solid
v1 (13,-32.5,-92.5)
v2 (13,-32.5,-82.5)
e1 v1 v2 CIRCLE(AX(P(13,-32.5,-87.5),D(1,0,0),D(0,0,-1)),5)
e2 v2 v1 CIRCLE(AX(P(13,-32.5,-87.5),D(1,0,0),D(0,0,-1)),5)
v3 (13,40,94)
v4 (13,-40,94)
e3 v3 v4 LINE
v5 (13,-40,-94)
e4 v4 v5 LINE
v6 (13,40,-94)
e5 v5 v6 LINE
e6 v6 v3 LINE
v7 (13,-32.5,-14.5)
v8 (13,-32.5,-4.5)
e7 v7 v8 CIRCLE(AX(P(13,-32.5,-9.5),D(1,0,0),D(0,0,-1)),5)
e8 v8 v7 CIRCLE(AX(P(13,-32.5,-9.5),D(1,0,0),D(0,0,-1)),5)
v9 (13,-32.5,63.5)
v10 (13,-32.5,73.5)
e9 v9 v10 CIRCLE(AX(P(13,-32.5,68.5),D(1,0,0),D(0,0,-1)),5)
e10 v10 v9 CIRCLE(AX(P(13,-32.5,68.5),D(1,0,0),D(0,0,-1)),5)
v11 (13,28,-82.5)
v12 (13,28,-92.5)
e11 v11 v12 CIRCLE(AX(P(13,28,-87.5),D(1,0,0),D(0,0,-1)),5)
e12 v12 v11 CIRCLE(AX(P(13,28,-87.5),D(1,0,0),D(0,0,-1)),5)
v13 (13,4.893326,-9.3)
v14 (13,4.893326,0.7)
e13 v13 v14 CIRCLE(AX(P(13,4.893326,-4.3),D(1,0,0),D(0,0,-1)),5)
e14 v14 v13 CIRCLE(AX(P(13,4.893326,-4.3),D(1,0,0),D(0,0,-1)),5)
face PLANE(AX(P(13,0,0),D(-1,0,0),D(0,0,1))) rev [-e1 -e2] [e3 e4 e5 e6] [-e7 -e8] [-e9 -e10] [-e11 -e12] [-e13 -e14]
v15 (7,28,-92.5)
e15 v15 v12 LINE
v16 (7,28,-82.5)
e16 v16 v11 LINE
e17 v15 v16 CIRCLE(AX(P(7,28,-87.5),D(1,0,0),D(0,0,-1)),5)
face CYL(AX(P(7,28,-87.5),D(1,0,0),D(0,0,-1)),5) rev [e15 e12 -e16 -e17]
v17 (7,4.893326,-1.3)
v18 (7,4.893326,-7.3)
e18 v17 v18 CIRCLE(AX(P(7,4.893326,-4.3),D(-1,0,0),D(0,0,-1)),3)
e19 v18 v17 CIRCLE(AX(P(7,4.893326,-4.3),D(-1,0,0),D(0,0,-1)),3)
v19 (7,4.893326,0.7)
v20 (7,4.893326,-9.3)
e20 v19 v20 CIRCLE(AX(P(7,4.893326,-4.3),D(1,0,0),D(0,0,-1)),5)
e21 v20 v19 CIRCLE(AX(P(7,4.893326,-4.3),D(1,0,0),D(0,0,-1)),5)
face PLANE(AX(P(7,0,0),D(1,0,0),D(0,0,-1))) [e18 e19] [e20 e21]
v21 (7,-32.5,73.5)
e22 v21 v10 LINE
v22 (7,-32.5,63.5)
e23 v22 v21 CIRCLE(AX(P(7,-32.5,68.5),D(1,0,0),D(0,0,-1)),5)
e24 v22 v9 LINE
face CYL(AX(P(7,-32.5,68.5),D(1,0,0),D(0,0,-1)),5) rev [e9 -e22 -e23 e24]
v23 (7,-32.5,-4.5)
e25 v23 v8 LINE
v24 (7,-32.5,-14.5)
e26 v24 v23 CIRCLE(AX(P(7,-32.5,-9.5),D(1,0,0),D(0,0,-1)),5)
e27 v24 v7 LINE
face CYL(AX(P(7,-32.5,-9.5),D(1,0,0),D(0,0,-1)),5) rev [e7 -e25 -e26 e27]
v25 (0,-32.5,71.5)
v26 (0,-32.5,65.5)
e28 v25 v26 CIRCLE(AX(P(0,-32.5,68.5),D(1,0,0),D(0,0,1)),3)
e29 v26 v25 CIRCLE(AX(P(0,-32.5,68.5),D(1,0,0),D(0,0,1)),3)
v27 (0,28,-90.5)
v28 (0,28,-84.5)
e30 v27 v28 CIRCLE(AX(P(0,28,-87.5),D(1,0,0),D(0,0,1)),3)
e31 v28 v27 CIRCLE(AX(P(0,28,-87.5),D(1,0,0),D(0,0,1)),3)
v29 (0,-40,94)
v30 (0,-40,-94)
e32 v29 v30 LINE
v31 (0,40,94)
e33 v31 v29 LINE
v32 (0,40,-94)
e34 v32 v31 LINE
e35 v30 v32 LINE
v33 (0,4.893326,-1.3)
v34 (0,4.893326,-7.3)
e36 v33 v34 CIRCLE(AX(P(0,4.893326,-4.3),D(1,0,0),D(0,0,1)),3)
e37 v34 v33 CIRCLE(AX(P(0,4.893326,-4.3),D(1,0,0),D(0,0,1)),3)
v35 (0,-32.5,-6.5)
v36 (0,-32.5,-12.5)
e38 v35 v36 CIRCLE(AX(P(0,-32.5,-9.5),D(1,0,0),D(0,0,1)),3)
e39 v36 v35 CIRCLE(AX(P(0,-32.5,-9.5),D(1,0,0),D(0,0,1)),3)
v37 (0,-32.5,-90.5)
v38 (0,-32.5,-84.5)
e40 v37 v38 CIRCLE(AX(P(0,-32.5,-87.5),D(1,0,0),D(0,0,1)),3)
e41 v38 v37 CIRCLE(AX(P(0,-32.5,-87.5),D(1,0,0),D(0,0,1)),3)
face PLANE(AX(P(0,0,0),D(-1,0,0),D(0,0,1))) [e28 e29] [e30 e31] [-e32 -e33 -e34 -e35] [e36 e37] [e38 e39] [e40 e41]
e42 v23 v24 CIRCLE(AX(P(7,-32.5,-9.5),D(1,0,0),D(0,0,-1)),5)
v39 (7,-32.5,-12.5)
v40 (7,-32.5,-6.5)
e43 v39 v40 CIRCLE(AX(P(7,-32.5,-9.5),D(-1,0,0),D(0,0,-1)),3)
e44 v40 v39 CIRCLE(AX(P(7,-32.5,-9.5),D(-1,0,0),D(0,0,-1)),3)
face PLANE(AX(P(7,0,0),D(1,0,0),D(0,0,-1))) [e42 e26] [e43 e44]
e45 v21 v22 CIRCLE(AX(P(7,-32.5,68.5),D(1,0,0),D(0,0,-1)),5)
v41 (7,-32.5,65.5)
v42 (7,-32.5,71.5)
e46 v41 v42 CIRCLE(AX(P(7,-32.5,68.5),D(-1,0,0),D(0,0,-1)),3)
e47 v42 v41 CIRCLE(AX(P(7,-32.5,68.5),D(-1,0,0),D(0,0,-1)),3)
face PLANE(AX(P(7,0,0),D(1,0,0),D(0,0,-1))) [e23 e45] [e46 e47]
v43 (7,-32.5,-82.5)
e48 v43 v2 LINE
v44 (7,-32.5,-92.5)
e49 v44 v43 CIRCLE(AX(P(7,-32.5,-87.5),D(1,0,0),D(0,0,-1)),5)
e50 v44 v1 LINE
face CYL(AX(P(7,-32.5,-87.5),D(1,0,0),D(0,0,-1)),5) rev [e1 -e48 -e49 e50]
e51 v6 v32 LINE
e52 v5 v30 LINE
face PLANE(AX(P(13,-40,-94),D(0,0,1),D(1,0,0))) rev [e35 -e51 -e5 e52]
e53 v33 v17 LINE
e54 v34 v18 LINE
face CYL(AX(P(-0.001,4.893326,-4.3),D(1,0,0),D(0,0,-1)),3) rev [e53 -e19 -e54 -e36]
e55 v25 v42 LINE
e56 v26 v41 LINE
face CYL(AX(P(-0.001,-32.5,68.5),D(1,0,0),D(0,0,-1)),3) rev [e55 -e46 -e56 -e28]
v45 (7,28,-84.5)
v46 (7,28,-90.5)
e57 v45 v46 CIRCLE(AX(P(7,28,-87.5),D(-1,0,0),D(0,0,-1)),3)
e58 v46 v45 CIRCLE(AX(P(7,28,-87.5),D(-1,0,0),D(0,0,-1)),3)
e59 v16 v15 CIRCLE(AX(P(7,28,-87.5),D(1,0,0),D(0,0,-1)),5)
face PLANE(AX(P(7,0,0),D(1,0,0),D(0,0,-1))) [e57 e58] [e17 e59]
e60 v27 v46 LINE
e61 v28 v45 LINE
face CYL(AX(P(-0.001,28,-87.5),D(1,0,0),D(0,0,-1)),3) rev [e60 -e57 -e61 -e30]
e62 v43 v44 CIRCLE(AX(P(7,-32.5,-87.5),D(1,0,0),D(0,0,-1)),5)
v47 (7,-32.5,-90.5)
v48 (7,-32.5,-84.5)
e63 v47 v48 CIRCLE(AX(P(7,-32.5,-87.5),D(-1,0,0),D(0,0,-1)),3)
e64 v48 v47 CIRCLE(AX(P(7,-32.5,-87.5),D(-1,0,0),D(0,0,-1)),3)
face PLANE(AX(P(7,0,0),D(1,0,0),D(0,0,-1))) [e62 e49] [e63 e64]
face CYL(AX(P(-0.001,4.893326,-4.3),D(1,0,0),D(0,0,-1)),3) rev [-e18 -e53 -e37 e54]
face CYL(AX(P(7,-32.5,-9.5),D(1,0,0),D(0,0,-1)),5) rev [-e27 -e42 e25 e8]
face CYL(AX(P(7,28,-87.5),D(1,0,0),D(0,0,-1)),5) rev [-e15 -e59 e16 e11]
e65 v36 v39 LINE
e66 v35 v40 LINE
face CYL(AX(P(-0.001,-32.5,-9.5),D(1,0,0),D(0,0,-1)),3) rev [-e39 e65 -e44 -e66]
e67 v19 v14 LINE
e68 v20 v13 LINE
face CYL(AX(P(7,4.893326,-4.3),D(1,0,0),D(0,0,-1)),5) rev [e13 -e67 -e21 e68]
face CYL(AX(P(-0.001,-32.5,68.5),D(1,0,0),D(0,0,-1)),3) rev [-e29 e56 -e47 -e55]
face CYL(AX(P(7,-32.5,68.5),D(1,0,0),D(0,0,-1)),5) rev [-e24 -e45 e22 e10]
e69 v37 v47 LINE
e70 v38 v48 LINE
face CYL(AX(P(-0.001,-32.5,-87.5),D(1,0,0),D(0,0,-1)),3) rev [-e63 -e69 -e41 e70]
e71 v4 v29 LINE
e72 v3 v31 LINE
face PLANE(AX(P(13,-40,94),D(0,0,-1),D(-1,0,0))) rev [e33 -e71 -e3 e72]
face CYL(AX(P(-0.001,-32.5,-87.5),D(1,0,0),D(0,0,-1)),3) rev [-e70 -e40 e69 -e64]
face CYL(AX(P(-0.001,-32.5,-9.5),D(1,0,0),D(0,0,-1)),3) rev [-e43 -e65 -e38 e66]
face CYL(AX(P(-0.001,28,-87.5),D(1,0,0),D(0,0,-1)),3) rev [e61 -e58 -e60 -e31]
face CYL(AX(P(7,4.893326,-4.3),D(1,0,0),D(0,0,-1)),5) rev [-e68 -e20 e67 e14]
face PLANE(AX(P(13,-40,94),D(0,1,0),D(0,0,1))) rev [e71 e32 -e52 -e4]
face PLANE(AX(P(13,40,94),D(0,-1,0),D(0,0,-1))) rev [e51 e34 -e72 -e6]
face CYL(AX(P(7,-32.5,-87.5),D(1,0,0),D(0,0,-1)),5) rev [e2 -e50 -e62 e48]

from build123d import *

# Parameters (mm, degrees)
SKETCH1_W           = 188
SKETCH1_H           = 80
BOSS_EXTRUDE1_DEPTH = 13
SKETCH3_R           = 5
SKETCH3_R_2         = 3
CUT_EXTRUDE1_DEPTH  = 6
CUT_EXTRUDE2_REACH  = 104.981
SKETCH3_3_R         = 3
SKETCH4_R           = 5
SKETCH4_R_2         = 3
CUT_EXTRUDE3_DEPTH  = 6
CUT_EXTRUDE4_REACH  = 104.981
SKETCH4_3_R         = 3
SKETCH5_R           = 5
SKETCH5_R_2         = 3
CUT_EXTRUDE5_DEPTH  = 6
CUT_EXTRUDE6_REACH  = 104.981
SKETCH5_3_R         = 3


with BuildPart() as part:
    # Sketch1 → Boss-Extrude1 (new body)
    with BuildSketch(Plane(origin=(0, 0, 0), x_dir=(0, 0, -1), z_dir=(1, 0, 0))):
        Rectangle(SKETCH1_W, SKETCH1_H)
    extrude(amount=BOSS_EXTRUDE1_DEPTH)

    # Sketch3 → Cut-Extrude1 (cut)
    with BuildSketch(Plane(origin=(13, 0, 0), x_dir=(0, 0, -1), z_dir=(1, 0, 0))):
        with Locations((4.3, 4.893325501)):
            Circle(SKETCH3_R)
        with Locations((4.3, 4.893325501)):
            Circle(SKETCH3_R_2, mode=Mode.SUBTRACT)
    extrude(amount=-CUT_EXTRUDE1_DEPTH, mode=Mode.SUBTRACT)

    # Sketch3<3> → Cut-Extrude2 (cut, up to next)
    with BuildSketch(Plane(origin=(13, 0, 0), x_dir=(0, 0, -1), z_dir=(1, 0, 0)), mode=Mode.PRIVATE) as cut_extrude2_sk1:
        with Locations((4.3, 4.893325501)):
            Circle(SKETCH3_3_R)
    cut_extrude2_tool1 = extrude(cut_extrude2_sk1.sketch, amount=-CUT_EXTRUDE2_REACH, mode=Mode.PRIVATE) & part.part
    add(cut_extrude2_tool1.solids().sort_by_distance((13, 4.893326, -4.3))[0], mode=Mode.SUBTRACT)

    # Sketch4 → Cut-Extrude3 (cut)
    # profile 1 of 3: a face of its own
    with BuildSketch(Plane(origin=(13, 0, 0), x_dir=(0, 0, -1), z_dir=(1, 0, 0))):
        with Locations((-68.5, -32.5)):
            Circle(SKETCH4_R)
        with Locations((-68.5, -32.5)):
            Circle(SKETCH4_R_2, mode=Mode.SUBTRACT)
    # profile 2 of 3: a face of its own
    with BuildSketch(Plane(origin=(13, 0, 0), x_dir=(0, 0, -1), z_dir=(1, 0, 0))):
        with Locations((9.5, -32.5)):
            Circle(SKETCH4_R)
        with Locations((9.5, -32.5)):
            Circle(SKETCH4_R_2, mode=Mode.SUBTRACT)
    # profile 3 of 3: a face of its own
    with BuildSketch(Plane(origin=(13, 0, 0), x_dir=(0, 0, -1), z_dir=(1, 0, 0))):
        with Locations((87.5, -32.5)):
            Circle(SKETCH4_R)
        with Locations((87.5, -32.5)):
            Circle(SKETCH4_R_2, mode=Mode.SUBTRACT)
    extrude(amount=-CUT_EXTRUDE3_DEPTH, mode=Mode.SUBTRACT)

    # Sketch4<3> → Cut-Extrude4 (cut, up to next)
    with BuildSketch(Plane(origin=(13, 0, 0), x_dir=(0, 0, -1), z_dir=(1, 0, 0)), mode=Mode.PRIVATE) as cut_extrude4_sk1:
        with Locations((-68.5, -32.5)):
            Circle(SKETCH4_3_R)
    cut_extrude4_tool1 = extrude(cut_extrude4_sk1.sketch, amount=-CUT_EXTRUDE4_REACH, mode=Mode.PRIVATE) & part.part
    # Sketch4<3> → Cut-Extrude4 (cut, up to next)
    with BuildSketch(Plane(origin=(13, 0, 0), x_dir=(0, 0, -1), z_dir=(1, 0, 0)), mode=Mode.PRIVATE) as cut_extrude4_sk2:
        with Locations((9.5, -32.5)):
            Circle(SKETCH4_3_R)
    cut_extrude4_tool2 = extrude(cut_extrude4_sk2.sketch, amount=-CUT_EXTRUDE4_REACH, mode=Mode.PRIVATE) & part.part
    # Sketch4<3> → Cut-Extrude4 (cut, up to next)
    with BuildSketch(Plane(origin=(13, 0, 0), x_dir=(0, 0, -1), z_dir=(1, 0, 0)), mode=Mode.PRIVATE) as cut_extrude4_sk3:
        with Locations((87.5, -32.5)):
            Circle(SKETCH4_3_R)
    cut_extrude4_tool3 = extrude(cut_extrude4_sk3.sketch, amount=-CUT_EXTRUDE4_REACH, mode=Mode.PRIVATE) & part.part
    add(cut_extrude4_tool1.solids().sort_by_distance((13, -32.5, 68.5))[0], mode=Mode.SUBTRACT)
    add(cut_extrude4_tool2.solids().sort_by_distance((13, -32.5, -9.5))[0], mode=Mode.SUBTRACT)
    add(cut_extrude4_tool3.solids().sort_by_distance((13, -32.5, -87.5))[0], mode=Mode.SUBTRACT)

    # Sketch5 → Cut-Extrude5 (cut)
    with BuildSketch(Plane(origin=(13, 0, 0), x_dir=(0, 0, -1), z_dir=(1, 0, 0))):
        with Locations((87.5, 28)):
            Circle(SKETCH5_R)
        with Locations((87.5, 28)):
            Circle(SKETCH5_R_2, mode=Mode.SUBTRACT)
    extrude(amount=-CUT_EXTRUDE5_DEPTH, mode=Mode.SUBTRACT)

    # Sketch5<3> → Cut-Extrude6 (cut, up to next)
    with BuildSketch(Plane(origin=(13, 0, 0), x_dir=(0, 0, -1), z_dir=(1, 0, 0)), mode=Mode.PRIVATE) as cut_extrude6_sk1:
        with Locations((87.5, 28)):
            Circle(SKETCH5_3_R)
    cut_extrude6_tool1 = extrude(cut_extrude6_sk1.sketch, amount=-CUT_EXTRUDE6_REACH, mode=Mode.PRIVATE) & part.part
    add(cut_extrude6_tool1.solids().sort_by_distance((13, 28, -87.5))[0], mode=Mode.SUBTRACT)


solid = part.part
